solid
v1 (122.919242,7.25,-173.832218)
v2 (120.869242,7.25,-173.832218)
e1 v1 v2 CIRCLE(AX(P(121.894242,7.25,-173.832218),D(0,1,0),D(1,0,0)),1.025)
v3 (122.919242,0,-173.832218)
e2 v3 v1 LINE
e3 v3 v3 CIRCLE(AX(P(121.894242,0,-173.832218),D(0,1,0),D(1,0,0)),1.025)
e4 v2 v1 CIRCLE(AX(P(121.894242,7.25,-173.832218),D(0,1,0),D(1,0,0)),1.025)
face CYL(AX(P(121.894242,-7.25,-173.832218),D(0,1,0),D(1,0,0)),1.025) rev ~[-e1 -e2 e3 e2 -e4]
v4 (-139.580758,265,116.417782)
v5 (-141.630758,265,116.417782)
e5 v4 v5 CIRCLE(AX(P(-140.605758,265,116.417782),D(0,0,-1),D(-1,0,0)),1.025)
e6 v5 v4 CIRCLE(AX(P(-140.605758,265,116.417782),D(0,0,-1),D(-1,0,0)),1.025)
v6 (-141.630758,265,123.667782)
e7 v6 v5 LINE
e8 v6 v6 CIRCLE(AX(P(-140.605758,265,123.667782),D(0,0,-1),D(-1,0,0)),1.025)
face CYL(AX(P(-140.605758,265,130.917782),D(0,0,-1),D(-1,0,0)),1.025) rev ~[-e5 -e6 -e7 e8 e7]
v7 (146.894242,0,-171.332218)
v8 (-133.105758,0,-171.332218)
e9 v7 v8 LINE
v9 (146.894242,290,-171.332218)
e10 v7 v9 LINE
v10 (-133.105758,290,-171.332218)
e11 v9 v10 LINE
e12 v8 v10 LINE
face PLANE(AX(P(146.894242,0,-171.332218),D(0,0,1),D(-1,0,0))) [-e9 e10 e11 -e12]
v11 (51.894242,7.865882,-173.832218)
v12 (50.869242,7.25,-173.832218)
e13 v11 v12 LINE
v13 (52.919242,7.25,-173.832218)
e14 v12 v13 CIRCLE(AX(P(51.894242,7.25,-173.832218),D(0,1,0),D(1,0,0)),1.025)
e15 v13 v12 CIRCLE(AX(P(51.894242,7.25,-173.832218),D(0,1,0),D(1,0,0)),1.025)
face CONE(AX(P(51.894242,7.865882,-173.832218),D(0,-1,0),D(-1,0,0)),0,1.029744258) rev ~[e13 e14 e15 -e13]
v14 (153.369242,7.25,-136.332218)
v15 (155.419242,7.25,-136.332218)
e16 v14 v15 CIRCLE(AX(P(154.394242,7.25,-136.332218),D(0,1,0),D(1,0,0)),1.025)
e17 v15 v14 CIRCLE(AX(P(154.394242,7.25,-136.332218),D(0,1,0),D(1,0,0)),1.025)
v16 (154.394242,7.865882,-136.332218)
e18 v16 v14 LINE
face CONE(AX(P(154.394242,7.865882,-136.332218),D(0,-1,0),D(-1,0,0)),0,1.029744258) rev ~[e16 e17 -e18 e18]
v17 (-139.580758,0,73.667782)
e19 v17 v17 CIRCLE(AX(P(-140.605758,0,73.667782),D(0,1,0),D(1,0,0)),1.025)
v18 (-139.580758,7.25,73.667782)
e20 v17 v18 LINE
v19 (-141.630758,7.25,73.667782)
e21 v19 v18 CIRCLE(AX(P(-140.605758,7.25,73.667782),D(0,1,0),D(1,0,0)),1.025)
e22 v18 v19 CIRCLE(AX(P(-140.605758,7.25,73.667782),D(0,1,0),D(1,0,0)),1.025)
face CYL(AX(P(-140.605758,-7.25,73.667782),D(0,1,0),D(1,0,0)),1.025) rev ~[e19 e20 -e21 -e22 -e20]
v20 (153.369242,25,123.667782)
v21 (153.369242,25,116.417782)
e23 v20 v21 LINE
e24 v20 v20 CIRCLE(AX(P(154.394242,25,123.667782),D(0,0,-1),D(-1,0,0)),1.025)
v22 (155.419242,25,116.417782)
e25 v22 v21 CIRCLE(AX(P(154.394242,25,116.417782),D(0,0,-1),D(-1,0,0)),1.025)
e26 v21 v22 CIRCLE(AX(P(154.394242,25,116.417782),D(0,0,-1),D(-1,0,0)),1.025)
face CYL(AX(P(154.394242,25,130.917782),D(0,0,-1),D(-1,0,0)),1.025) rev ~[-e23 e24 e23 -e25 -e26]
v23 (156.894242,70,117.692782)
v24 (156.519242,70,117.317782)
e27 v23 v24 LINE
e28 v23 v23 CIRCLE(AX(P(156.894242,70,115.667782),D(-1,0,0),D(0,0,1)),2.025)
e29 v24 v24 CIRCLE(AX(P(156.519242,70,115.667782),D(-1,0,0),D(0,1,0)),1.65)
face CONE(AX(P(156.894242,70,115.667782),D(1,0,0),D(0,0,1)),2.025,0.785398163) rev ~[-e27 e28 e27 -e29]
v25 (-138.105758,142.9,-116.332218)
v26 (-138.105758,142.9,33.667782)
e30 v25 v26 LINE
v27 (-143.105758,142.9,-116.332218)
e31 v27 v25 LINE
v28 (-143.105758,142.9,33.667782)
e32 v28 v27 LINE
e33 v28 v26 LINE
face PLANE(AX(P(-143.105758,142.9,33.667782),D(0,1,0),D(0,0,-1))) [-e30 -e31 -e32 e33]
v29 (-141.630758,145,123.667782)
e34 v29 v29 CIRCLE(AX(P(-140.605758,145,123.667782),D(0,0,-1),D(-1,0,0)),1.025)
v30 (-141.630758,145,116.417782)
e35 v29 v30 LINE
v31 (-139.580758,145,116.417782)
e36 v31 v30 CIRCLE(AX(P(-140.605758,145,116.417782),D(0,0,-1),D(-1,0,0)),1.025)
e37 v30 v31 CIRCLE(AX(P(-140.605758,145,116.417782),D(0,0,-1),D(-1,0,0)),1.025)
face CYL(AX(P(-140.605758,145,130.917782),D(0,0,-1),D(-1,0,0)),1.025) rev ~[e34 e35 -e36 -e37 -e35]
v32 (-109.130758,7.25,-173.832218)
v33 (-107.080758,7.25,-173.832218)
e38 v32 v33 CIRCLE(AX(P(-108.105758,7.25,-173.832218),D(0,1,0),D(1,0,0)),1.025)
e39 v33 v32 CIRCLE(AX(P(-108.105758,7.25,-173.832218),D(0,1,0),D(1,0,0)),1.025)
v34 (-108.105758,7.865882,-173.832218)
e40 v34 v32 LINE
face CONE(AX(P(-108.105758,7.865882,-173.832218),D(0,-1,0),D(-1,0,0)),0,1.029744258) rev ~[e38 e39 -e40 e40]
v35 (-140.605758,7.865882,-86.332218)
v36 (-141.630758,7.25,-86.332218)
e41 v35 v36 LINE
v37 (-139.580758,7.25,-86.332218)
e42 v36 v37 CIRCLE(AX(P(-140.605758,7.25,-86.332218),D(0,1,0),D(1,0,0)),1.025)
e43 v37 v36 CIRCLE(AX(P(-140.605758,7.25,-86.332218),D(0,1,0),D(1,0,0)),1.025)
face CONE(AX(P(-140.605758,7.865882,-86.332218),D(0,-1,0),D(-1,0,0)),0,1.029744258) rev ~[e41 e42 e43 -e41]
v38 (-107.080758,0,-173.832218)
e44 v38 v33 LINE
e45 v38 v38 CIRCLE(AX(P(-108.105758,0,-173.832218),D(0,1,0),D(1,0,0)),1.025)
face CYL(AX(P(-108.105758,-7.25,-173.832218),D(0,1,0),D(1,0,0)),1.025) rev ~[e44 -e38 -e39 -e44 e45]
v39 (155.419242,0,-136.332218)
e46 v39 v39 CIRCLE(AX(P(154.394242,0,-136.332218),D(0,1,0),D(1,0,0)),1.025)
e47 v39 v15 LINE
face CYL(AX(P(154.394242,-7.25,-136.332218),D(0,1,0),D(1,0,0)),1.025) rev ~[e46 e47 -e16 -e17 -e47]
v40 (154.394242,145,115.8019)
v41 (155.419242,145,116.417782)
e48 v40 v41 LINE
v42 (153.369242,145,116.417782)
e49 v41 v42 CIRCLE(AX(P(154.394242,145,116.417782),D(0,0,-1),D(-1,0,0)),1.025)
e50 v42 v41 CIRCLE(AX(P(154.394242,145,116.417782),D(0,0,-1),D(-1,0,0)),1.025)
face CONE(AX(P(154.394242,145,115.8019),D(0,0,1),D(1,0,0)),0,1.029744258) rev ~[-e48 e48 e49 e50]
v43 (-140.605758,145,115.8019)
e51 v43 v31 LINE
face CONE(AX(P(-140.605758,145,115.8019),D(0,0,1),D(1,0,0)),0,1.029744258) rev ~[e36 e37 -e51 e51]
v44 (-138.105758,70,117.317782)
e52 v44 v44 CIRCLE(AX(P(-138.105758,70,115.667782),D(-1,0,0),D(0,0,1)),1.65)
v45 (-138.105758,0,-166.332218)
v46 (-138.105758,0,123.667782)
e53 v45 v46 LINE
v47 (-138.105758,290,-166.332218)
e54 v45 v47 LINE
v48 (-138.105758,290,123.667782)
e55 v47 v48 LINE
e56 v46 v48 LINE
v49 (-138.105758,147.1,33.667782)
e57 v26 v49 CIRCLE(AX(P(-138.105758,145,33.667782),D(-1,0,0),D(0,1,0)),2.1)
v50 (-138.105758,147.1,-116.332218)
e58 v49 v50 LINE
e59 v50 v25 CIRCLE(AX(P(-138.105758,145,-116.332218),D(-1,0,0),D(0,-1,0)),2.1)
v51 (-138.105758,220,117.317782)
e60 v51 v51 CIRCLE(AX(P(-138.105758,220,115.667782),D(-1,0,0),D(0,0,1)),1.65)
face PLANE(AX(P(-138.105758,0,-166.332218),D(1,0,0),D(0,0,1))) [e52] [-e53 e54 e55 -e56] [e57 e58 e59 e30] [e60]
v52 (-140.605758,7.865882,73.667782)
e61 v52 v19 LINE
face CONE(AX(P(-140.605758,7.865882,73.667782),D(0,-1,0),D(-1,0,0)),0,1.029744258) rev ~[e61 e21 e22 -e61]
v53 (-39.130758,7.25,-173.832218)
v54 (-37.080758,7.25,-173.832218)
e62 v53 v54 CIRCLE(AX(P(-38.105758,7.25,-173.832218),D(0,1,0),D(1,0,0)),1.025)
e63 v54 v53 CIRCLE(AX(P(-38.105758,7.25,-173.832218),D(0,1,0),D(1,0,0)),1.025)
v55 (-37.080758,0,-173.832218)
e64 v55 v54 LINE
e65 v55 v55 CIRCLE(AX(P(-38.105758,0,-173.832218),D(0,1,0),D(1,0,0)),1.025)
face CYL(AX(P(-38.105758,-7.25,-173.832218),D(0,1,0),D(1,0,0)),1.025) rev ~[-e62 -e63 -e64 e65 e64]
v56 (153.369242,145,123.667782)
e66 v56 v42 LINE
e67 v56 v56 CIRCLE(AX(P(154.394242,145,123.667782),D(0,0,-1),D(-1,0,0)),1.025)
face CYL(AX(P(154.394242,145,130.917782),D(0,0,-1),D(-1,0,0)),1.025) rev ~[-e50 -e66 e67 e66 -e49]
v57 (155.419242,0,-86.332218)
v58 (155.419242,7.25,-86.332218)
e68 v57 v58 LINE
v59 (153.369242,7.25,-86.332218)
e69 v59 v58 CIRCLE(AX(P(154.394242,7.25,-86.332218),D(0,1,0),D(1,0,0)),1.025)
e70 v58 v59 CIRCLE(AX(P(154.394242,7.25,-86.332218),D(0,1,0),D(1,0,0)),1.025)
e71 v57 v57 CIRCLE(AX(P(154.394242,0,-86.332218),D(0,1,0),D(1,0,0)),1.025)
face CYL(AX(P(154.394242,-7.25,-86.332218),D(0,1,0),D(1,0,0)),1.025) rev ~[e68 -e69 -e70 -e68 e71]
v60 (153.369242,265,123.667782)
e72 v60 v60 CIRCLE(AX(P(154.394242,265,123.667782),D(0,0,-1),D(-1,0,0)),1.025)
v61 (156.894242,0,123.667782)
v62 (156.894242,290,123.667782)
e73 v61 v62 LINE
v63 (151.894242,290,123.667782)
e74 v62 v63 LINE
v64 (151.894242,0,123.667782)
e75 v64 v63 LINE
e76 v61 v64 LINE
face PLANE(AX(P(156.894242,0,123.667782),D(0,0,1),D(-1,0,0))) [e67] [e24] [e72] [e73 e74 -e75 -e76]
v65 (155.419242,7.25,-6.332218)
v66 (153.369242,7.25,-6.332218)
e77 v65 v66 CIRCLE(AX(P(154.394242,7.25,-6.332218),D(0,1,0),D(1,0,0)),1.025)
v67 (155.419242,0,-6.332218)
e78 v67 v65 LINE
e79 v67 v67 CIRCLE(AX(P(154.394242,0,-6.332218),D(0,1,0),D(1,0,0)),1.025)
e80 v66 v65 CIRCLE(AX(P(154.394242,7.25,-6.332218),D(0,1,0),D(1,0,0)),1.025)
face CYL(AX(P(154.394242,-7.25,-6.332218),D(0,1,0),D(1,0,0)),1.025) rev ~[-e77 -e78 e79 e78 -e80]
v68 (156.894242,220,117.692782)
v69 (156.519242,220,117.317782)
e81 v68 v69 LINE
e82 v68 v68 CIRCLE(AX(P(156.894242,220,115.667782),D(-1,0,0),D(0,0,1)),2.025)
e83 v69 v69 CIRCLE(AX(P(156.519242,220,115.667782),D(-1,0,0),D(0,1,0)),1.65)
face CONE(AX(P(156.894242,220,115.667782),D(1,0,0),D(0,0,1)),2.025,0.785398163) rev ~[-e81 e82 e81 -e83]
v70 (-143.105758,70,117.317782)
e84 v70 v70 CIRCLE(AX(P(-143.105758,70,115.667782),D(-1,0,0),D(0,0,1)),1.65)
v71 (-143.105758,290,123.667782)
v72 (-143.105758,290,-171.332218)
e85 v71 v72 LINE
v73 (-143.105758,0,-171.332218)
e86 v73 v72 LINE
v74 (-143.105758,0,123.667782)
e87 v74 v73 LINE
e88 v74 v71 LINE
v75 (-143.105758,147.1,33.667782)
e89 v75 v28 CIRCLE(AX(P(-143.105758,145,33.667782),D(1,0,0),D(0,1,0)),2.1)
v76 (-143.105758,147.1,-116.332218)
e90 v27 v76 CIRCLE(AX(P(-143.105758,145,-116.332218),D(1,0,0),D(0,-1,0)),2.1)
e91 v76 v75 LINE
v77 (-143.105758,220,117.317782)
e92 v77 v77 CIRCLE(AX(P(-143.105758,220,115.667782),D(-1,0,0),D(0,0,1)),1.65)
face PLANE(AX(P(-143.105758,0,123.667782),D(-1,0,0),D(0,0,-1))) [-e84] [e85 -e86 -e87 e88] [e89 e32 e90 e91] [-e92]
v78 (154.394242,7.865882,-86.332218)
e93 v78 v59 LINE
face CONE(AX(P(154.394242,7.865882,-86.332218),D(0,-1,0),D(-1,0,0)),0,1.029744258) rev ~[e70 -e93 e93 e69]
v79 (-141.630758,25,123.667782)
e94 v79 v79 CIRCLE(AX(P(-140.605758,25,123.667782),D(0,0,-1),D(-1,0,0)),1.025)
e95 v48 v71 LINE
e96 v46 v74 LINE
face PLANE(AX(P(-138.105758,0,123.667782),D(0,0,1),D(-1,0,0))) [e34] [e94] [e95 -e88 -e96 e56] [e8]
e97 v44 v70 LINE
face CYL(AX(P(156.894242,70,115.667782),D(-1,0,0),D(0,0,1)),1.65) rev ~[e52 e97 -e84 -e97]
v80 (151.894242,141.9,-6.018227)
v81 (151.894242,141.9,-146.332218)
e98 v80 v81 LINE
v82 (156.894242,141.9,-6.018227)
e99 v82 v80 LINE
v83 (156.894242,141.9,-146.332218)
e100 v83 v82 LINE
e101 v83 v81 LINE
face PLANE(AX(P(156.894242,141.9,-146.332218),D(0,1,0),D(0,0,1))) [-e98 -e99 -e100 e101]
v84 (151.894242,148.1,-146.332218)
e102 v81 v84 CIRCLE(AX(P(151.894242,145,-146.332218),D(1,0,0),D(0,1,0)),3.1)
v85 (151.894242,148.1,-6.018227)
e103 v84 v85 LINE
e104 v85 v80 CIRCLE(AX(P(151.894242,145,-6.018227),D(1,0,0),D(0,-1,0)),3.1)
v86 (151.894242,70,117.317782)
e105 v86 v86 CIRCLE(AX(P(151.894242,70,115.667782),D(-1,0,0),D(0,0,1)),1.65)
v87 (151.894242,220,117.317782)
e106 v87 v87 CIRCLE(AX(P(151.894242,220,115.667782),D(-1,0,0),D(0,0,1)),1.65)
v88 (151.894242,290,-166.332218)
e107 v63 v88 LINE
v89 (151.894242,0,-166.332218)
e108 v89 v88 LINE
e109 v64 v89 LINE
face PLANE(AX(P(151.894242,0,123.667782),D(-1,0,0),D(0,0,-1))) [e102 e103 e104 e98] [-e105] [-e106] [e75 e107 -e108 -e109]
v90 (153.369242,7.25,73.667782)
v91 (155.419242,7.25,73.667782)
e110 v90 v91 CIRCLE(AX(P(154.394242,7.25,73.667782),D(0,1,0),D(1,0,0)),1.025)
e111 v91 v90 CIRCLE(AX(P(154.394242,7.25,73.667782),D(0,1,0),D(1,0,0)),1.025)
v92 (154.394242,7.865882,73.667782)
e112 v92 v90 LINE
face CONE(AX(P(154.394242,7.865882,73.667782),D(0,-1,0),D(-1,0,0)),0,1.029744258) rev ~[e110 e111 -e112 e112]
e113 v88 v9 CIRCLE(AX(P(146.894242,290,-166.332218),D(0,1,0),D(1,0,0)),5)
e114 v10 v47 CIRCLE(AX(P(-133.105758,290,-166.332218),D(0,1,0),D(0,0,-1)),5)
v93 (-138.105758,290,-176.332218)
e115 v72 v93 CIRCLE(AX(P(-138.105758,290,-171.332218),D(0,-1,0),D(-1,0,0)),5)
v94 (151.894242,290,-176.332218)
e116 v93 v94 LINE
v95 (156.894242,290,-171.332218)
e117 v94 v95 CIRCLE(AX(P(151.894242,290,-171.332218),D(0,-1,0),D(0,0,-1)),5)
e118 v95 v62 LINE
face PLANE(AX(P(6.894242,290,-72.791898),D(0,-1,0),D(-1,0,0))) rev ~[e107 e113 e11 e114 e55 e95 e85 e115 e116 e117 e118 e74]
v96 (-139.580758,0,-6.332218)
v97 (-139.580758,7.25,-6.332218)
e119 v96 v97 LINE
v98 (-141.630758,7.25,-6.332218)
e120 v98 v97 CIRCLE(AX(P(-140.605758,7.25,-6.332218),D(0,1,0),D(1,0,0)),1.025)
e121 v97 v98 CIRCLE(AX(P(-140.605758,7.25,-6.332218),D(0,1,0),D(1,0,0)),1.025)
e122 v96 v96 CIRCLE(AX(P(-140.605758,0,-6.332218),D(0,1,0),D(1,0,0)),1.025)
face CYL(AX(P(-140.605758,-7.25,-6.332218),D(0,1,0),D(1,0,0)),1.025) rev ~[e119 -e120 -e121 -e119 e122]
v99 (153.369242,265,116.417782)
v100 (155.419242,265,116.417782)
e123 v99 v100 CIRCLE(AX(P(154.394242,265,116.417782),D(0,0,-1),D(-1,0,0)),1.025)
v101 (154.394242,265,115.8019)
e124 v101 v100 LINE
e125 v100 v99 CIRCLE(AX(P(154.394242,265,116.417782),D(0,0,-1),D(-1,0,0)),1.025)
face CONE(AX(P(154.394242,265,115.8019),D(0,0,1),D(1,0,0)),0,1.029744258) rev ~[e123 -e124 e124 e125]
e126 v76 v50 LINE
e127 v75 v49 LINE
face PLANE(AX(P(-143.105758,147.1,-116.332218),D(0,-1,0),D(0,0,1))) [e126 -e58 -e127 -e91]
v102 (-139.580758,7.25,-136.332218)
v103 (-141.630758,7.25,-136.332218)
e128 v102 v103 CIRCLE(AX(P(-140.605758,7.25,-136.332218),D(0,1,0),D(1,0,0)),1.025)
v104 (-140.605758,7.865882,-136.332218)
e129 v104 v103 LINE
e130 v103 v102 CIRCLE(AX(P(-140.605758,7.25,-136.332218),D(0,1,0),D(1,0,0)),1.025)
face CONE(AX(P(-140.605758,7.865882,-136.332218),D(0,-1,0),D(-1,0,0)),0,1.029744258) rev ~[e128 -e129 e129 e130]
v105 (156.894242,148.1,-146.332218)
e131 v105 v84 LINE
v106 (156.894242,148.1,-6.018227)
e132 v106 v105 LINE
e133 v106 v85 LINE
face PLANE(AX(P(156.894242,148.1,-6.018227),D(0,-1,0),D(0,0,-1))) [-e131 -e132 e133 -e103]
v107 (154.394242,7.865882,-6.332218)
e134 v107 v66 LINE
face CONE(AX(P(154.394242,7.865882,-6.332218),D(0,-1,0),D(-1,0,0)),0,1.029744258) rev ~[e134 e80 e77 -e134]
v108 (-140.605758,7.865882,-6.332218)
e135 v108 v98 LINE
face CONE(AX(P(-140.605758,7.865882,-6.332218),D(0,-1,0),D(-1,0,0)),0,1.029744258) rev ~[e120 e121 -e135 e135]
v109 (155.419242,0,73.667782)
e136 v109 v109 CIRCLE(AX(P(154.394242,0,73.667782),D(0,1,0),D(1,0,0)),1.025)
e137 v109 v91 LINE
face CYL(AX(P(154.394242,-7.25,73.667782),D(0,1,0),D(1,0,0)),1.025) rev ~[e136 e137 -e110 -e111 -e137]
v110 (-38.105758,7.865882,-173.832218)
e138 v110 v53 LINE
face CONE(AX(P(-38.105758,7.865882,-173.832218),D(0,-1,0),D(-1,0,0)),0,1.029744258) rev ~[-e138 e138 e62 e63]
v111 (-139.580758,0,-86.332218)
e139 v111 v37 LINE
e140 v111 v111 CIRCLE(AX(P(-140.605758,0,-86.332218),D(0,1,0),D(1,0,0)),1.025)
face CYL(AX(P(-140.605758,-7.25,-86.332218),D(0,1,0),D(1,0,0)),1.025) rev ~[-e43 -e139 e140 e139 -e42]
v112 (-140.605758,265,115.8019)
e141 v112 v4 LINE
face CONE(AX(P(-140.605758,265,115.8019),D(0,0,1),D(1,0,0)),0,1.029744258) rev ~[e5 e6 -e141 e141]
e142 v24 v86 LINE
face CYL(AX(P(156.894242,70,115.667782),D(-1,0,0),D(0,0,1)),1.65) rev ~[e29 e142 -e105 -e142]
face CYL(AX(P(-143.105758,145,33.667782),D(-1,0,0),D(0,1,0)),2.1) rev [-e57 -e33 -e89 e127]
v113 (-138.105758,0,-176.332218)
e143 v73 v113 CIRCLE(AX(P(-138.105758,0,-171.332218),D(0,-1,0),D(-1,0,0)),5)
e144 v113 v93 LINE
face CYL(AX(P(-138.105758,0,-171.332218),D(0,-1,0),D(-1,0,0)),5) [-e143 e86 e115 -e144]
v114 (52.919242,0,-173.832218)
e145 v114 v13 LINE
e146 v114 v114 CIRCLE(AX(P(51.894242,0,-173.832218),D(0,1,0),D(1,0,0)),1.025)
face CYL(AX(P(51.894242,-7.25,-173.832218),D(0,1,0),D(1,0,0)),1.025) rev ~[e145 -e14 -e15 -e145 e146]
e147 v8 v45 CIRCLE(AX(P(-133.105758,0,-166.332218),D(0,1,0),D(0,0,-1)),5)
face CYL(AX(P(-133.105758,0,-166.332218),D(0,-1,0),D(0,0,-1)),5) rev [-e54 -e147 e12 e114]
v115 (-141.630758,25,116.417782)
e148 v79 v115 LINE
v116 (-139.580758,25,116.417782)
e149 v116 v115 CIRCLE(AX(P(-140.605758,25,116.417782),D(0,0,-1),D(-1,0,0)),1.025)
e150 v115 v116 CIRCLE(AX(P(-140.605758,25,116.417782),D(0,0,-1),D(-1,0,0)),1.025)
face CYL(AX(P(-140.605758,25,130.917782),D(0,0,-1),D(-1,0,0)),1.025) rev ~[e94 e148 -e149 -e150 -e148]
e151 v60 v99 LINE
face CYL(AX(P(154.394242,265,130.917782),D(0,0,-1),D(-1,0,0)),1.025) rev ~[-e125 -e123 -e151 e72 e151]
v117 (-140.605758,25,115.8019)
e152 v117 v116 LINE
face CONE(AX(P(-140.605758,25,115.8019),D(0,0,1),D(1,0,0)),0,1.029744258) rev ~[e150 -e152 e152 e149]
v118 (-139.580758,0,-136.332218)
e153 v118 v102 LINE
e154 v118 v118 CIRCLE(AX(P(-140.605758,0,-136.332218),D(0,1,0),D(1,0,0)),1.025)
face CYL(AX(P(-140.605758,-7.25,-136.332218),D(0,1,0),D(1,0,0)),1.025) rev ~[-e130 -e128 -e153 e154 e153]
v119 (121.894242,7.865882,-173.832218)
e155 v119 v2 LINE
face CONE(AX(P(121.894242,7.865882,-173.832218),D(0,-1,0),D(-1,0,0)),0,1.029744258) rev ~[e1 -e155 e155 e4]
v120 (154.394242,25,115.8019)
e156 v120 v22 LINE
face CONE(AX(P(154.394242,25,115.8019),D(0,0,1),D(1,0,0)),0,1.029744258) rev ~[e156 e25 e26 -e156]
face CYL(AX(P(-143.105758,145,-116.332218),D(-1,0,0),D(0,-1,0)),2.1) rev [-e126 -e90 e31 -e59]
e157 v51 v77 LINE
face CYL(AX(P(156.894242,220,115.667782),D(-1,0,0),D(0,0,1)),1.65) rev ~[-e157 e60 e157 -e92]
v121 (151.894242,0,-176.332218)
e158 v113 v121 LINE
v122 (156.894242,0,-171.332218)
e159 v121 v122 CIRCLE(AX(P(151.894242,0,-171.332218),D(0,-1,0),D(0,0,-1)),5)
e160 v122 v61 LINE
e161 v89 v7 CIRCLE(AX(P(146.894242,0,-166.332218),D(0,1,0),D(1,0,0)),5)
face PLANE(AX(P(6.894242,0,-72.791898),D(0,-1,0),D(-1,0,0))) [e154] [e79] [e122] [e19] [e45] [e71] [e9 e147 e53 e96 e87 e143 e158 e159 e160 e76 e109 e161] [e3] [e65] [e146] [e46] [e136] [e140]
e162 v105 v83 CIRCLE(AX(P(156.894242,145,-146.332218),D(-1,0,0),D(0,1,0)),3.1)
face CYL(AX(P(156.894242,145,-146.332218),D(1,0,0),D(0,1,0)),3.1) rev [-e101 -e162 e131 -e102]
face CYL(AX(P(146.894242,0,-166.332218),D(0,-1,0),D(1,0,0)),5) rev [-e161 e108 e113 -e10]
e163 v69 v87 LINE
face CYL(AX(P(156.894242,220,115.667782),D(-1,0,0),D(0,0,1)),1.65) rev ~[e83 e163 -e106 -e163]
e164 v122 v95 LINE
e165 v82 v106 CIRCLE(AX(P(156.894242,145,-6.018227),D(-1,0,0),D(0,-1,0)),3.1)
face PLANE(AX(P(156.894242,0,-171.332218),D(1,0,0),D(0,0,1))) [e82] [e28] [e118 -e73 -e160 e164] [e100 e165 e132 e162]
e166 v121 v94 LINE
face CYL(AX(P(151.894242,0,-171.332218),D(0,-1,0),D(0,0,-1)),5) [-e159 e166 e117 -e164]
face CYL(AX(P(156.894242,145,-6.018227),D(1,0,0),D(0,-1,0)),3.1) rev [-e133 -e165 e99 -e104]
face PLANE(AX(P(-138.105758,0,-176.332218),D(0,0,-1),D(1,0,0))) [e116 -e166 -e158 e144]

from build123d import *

# Parameters (mm, degrees)
BOSS_EXTRUDE1_DEPTH         = 290
M2_5_TAPPED_HOLE1_D         = 2.05
M2_5_TAPPED_HOLE1_DEPTH     = 7.25
M2_5_TAPPED_HOLE1_TIP       = 0.615882135
CUT_EXTRUDE2_DEPTH          = 41
CUT_EXTRUDE3_DEPTH          = 56
M4_TAPPED_HOLE1_D           = 3.3
M4_TAPPED_HOLE1_CSINK_D     = 4.05
M4_TAPPED_HOLE1_CSINK_ANGLE = 90
M2_5_TAPPED_HOLE2_D         = 2.05
M2_5_TAPPED_HOLE2_DEPTH     = 7.25
M2_5_TAPPED_HOLE2_TIP       = 0.615882135


with BuildPart() as part:
    # Sketch1 → Boss-Extrude1 (new body)
    with BuildSketch(Plane(origin=(0, 0, 0), x_dir=(1, 0, 0), z_dir=(0, 1, 0))):
        with BuildLine():
            Line((-138.105758434, 176.332217748), (151.894241566, 176.332217748))
            ThreePointArc((151.894241566, 176.332217748), (155.429775472, 174.867751654), (156.894241566, 171.332217748))
            Line((156.894241566, 171.332217748), (156.894241566, -123.667782252))
            Line((156.894241566, -123.667782252), (151.894241566, -123.667782252))
            Line((151.894241566, -123.667782252), (151.894241566, 166.332217748))
            ThreePointArc((151.894241566, 166.332217748), (150.429775472, 169.867751654), (146.894241566, 171.332217748))
            Line((146.894241566, 171.332217748), (-133.105758434, 171.332217748))
            ThreePointArc((-133.105758434, 171.332217748), (-136.64129234, 169.867751654), (-138.105758434, 166.332217748))
            Line((-138.105758434, 166.332217748), (-138.105758434, -123.667782252))
            Line((-138.105758434, -123.667782252), (-143.105758434, -123.667782252))
            Line((-143.105758434, -123.667782252), (-143.105758434, 171.332217748))
            ThreePointArc((-143.105758434, 171.332217748), (-141.64129234, 174.867751654), (-138.105758434, 176.332217748))
        make_face()
    extrude(amount=BOSS_EXTRUDE1_DEPTH)

    # M2.5 Tapped Hole1
    with Locations(Plane.XY.offset(123.667782252)):
        with Locations((-140.605758434, 145), (-140.605758434, 265), (-140.605758434, 25), (154.394241566, 145), (154.394241566, 265), (154.394241566, 25)):
            Hole(M2_5_TAPPED_HOLE1_D / 2, depth=M2_5_TAPPED_HOLE1_DEPTH)
            with Locations((0, 0, -(M2_5_TAPPED_HOLE1_DEPTH + M2_5_TAPPED_HOLE1_TIP / 2))):  # 118° drill point
                Cone(0, M2_5_TAPPED_HOLE1_D / 2, M2_5_TAPPED_HOLE1_TIP, mode=Mode.SUBTRACT)

    # Sketch5 → Cut-Extrude2 (cut)
    with BuildSketch(Plane.ZY.offset(143.105758434)):
        with BuildLine():
            Line((-116.332217748, 147.1), (33.667782252, 147.1))
            ThreePointArc((33.667782252, 147.1), (35.767782252, 145), (33.667782252, 142.9))
            Line((33.667782252, 142.9), (-116.332217748, 142.9))
            ThreePointArc((-116.332217748, 142.9), (-118.432217748, 145), (-116.332217748, 147.1))
        make_face()
    extrude(amount=-CUT_EXTRUDE2_DEPTH, mode=Mode.SUBTRACT)

    # Sketch6 → Cut-Extrude3 (cut)
    with BuildSketch(Plane(origin=(156.894241566, 0, 0), x_dir=(0, 0, -1), z_dir=(1, 0, 0))):
        with BuildLine():
            Line((6.018226887, 148.1), (146.332217748, 148.1))
            ThreePointArc((146.332217748, 148.1), (149.432217748, 145), (146.332217748, 141.9))
            Line((146.332217748, 141.9), (6.018226887, 141.9))
            ThreePointArc((6.018226887, 141.9), (2.918226887, 145), (6.018226887, 148.1))
        make_face()
    extrude(amount=-CUT_EXTRUDE3_DEPTH, mode=Mode.SUBTRACT)

    # M4 Tapped Hole1 (through all)
    with Locations(Plane(origin=(156.894241566, 0, 0), x_dir=(0, 0, -1), z_dir=(1, 0, 0))):
        with Locations((-115.667782252, 220), (-115.667782252, 70)):
            CounterSinkHole(M4_TAPPED_HOLE1_D / 2, M4_TAPPED_HOLE1_CSINK_D / 2, counter_sink_angle=M4_TAPPED_HOLE1_CSINK_ANGLE)

    # M2.5 Tapped Hole2
    with Locations(Plane(origin=(0, 0, 0), x_dir=(-1, 0, 0), z_dir=(0, -1, 0))):
        with Locations((-154.394241566, 136.332217748), (-154.394241566, 86.332217748), (-154.394241566, 6.332217748), (-154.394241566, -73.667782252), (-121.894241566, 173.832217748), (-51.894241566, 173.832217748), (38.105758434, 173.832217748), (108.105758434, 173.832217748), (140.605758434, -73.667782252), (140.605758434, 6.332217748), (140.605758434, 86.332217748), (140.605758434, 136.332217748)):
            Hole(M2_5_TAPPED_HOLE2_D / 2, depth=M2_5_TAPPED_HOLE2_DEPTH)
            with Locations((0, 0, -(M2_5_TAPPED_HOLE2_DEPTH + M2_5_TAPPED_HOLE2_TIP / 2))):  # 118° drill point
                Cone(0, M2_5_TAPPED_HOLE2_D / 2, M2_5_TAPPED_HOLE2_TIP, mode=Mode.SUBTRACT)


solid = part.part
